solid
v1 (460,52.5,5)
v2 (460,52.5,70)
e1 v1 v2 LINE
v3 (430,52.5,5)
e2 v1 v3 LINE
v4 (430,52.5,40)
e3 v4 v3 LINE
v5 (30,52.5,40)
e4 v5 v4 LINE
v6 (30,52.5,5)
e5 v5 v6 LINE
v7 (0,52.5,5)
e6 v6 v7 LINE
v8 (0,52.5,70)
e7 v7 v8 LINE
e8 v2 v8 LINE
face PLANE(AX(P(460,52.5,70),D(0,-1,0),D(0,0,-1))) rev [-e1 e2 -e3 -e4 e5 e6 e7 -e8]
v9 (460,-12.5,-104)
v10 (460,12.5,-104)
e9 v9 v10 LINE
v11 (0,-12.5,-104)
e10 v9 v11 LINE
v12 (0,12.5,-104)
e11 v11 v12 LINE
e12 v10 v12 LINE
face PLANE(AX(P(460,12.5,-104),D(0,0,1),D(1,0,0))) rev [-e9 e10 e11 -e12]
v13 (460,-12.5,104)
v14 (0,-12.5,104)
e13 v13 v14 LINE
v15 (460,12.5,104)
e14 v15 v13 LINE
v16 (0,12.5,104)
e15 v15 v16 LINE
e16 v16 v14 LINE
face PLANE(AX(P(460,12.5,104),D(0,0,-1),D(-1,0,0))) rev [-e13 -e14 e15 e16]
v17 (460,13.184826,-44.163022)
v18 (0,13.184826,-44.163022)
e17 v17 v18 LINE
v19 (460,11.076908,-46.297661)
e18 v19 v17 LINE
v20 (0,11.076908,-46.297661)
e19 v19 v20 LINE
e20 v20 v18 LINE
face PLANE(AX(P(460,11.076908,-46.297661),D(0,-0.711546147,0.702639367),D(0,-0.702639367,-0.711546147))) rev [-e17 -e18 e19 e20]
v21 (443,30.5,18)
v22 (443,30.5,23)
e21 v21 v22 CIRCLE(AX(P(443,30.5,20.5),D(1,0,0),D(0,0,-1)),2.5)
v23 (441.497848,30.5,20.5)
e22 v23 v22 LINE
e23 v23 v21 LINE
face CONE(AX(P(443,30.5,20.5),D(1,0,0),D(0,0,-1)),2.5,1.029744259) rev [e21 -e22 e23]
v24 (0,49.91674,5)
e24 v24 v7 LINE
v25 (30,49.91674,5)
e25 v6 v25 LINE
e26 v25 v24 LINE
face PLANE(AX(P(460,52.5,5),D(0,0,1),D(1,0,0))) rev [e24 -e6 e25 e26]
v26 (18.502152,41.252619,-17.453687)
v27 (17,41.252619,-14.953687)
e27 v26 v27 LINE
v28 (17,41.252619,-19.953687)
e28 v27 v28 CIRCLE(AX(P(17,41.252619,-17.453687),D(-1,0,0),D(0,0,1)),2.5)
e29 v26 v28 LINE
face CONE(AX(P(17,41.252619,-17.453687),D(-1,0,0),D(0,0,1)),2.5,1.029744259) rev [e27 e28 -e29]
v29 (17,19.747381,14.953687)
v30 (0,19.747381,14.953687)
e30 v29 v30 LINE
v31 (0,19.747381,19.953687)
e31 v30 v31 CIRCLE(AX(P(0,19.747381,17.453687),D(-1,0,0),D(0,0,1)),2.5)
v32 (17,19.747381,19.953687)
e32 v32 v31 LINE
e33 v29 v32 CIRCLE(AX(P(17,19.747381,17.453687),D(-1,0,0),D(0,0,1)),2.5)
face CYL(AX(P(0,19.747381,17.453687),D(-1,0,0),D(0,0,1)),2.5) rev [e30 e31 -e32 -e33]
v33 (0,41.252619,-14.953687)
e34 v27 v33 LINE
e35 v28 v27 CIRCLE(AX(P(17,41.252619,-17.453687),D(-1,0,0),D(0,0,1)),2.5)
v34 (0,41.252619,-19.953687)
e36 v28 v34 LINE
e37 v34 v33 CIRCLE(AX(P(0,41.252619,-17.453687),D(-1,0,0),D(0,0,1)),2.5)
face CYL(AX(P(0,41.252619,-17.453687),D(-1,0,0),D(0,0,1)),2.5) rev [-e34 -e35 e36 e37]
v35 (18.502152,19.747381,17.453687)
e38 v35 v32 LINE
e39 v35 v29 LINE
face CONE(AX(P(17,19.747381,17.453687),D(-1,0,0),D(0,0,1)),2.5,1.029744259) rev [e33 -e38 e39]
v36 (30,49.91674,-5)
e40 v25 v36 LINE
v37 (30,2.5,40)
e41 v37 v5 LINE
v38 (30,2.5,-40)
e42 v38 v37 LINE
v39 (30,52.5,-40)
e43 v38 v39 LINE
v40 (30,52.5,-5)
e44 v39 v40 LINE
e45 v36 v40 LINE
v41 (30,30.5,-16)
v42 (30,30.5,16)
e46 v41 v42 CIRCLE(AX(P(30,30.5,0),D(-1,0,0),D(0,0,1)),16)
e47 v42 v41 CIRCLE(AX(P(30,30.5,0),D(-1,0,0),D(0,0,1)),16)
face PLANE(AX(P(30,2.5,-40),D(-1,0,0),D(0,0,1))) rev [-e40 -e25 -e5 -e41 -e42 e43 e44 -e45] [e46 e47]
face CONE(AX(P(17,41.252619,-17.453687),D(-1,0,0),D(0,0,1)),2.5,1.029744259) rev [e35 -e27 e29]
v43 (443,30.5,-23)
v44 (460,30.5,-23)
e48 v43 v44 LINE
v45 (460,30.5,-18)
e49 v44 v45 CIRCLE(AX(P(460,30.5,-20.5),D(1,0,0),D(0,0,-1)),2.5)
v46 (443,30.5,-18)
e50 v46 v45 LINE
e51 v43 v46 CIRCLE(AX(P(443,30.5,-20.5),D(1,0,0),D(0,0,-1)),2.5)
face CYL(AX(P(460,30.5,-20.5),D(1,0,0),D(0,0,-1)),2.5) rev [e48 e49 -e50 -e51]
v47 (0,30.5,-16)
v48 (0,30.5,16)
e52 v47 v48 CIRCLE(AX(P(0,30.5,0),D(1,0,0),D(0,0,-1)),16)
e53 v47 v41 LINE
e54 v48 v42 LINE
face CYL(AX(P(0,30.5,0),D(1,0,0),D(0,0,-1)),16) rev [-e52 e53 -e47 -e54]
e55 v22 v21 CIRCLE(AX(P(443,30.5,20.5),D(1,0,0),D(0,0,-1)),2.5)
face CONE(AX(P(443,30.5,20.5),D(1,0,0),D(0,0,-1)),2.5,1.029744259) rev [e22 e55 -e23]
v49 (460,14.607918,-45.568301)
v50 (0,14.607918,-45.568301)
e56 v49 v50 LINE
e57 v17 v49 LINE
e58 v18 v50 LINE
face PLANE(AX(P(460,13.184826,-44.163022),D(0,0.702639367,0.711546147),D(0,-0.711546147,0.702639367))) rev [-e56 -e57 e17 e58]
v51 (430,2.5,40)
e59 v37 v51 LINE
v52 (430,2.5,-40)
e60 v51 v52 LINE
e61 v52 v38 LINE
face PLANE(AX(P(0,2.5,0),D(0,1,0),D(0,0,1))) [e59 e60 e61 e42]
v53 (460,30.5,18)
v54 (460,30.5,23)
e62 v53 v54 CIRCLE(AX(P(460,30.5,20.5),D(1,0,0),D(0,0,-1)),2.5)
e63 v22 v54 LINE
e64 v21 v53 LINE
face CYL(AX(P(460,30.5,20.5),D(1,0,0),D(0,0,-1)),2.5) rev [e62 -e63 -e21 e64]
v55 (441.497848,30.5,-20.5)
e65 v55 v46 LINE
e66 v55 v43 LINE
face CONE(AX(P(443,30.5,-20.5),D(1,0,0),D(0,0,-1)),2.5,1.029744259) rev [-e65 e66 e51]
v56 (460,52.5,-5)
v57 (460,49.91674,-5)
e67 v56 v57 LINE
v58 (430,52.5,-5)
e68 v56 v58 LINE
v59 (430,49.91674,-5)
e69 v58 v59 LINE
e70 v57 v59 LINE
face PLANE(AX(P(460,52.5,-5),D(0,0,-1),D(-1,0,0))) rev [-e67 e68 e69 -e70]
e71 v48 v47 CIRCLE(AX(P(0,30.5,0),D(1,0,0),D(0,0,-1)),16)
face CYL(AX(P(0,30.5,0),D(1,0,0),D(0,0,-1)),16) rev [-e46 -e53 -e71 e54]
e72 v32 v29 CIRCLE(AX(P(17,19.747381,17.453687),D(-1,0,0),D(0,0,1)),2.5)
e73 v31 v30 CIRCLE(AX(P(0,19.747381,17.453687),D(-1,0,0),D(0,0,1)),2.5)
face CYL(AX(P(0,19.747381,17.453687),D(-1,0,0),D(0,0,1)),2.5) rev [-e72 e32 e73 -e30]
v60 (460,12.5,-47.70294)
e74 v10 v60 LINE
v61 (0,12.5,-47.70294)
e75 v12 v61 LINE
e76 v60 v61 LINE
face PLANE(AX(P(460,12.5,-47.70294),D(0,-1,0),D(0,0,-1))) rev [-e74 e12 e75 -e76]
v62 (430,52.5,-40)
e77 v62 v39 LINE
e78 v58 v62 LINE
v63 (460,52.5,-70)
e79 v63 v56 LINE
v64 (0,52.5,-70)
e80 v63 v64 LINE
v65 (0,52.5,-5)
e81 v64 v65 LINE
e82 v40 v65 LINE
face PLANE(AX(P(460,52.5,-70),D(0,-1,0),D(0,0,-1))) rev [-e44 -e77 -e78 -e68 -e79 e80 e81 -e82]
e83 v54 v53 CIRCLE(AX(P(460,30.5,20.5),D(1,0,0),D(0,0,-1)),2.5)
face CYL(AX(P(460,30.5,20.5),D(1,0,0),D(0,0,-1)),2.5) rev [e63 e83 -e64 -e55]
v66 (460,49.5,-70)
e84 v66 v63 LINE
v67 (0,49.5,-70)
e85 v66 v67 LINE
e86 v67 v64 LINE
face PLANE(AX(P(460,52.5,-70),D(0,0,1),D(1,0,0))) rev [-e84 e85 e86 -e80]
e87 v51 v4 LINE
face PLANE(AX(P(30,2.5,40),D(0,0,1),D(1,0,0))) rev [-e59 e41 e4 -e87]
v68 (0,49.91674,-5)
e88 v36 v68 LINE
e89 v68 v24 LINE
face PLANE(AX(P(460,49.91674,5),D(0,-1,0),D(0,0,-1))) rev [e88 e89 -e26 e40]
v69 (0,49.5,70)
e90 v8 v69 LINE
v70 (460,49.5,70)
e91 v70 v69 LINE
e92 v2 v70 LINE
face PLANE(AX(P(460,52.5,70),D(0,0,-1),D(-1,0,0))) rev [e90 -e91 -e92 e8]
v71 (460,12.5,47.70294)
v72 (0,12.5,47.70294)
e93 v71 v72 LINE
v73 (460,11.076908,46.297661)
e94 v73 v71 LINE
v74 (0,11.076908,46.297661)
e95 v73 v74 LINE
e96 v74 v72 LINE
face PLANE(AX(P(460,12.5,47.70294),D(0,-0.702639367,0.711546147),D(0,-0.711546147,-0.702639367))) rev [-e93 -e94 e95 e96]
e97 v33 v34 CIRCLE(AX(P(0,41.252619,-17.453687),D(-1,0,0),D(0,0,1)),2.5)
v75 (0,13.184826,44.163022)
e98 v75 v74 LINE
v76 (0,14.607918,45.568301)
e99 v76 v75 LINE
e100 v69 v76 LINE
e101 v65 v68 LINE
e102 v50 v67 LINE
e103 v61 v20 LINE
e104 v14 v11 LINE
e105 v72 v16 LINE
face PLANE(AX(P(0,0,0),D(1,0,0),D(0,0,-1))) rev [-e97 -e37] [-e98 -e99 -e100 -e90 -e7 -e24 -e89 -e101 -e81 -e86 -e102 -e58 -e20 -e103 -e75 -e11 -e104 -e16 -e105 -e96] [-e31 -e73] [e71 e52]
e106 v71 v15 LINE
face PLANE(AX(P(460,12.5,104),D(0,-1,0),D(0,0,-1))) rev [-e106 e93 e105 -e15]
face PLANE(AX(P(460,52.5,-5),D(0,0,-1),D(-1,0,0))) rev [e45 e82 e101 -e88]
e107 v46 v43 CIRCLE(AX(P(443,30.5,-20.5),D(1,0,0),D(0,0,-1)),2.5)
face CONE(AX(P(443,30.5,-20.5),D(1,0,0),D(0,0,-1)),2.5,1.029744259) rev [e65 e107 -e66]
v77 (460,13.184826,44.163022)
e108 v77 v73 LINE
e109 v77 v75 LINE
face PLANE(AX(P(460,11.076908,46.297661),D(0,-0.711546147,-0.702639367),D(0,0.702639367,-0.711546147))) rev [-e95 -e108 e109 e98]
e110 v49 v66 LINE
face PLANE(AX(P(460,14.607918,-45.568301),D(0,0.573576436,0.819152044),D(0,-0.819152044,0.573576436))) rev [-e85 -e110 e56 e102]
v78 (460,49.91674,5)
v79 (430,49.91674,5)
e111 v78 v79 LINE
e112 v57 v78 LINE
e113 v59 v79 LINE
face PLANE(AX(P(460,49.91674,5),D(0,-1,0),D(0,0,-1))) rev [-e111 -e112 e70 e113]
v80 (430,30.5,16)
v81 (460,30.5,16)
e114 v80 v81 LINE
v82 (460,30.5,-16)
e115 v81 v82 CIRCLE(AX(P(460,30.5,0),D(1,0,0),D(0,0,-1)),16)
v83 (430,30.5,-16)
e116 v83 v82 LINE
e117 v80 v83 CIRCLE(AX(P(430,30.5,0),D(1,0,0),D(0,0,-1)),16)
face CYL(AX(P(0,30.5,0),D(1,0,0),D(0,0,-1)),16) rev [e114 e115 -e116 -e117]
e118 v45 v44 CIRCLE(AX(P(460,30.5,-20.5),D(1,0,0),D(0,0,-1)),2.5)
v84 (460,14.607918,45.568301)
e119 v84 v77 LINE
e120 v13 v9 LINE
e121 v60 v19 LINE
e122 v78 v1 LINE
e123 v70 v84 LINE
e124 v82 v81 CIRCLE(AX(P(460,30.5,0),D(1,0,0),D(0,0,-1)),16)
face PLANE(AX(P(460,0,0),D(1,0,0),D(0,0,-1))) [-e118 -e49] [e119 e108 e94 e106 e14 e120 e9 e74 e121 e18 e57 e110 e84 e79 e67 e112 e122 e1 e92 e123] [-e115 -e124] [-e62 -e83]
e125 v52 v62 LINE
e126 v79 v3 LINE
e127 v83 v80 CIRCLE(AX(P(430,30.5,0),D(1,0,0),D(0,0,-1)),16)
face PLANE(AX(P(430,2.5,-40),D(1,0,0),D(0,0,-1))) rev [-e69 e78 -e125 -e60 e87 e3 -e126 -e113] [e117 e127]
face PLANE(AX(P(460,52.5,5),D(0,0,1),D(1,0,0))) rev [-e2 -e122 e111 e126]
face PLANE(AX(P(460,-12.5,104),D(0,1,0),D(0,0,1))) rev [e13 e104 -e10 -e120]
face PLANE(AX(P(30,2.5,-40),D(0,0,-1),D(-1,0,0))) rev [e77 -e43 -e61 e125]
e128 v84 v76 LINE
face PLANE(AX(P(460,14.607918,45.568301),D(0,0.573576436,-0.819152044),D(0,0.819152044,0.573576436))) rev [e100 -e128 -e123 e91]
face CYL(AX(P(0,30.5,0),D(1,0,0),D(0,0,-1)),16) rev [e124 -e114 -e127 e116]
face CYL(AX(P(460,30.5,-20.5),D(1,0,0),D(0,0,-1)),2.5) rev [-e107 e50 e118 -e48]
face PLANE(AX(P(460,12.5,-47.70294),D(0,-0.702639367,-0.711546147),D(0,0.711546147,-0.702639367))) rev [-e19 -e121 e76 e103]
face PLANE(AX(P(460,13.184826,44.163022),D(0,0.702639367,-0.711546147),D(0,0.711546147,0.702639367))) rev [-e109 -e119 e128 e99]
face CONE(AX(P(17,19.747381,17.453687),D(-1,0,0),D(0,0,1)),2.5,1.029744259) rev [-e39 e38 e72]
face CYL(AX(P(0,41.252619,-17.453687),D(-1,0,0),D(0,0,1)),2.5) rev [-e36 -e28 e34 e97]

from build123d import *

# Parameters (mm, degrees)
BOSS_EXTRUDE1_DEPTH   = 460
SKETCH2_W             = 400
SKETCH2_H             = 80
CUT_EXTRUDE1_DEPTH    = 50
SKETCH3_R             = 16
CUT_EXTRUDE2_DEPTH    = 475.523181731
M6_TAPPED_HOLE1_D     = 5
M6_TAPPED_HOLE1_DEPTH = 17
M6_TAPPED_HOLE1_TIP   = 1.502151548
M6_TAPPED_HOLE2_D     = 5
M6_TAPPED_HOLE2_DEPTH = 17
M6_TAPPED_HOLE2_TIP   = 1.502151548


with BuildPart() as part:
    # Sketch1 → Boss-Extrude1 (new body)
    with BuildSketch(Plane(origin=(0, 0, 0), x_dir=(0, 0, -1), z_dir=(1, 0, 0))):
        Polygon((-104, 12.5), (-47.702939672, 12.5), (-46.297660938, 11.076907706), (-44.163022497, 13.184825808), (-45.568301231, 14.607918102), (-70, 49.5), (-70, 52.5), (-5, 52.5), (-5, 49.916740154), (5, 49.916740154), (5, 52.5), (70, 52.5), (70, 49.5), (45.568301231, 14.607918102), (44.163022497, 13.184825808), (46.297660938, 11.076907706), (47.702939672, 12.5), (104, 12.5), (104, -12.5), (-104, -12.5), align=None)
    extrude(amount=BOSS_EXTRUDE1_DEPTH)

    # Sketch2 → Cut-Extrude1 (cut)
    with BuildSketch(Plane(origin=(0, 52.5, 0), x_dir=(1, 0, 0), z_dir=(0, 1, 0))):
        with Locations((230, 0)):
            Rectangle(SKETCH2_W, SKETCH2_H)
    extrude(amount=-CUT_EXTRUDE1_DEPTH, mode=Mode.SUBTRACT)

    # Sketch3 → Cut-Extrude2 (cut, through all)
    with BuildSketch(Plane(origin=(460, 0, 0), x_dir=(0, 0, -1), z_dir=(1, 0, 0))):
        with Locations((0, 30.5)):
            Circle(SKETCH3_R)
    extrude(amount=-CUT_EXTRUDE2_DEPTH, mode=Mode.SUBTRACT)

    # M6 Tapped Hole1
    with Locations(Plane(origin=(460, 0, 0), x_dir=(0, 0, -1), z_dir=(1, 0, 0))):
        with Locations((-20.5, 30.5), (20.5, 30.5)):
            Hole(M6_TAPPED_HOLE1_D / 2, depth=M6_TAPPED_HOLE1_DEPTH)
            with Locations((0, 0, -(M6_TAPPED_HOLE1_DEPTH + M6_TAPPED_HOLE1_TIP / 2))):  # 118° drill point
                Cone(0, M6_TAPPED_HOLE1_D / 2, M6_TAPPED_HOLE1_TIP, mode=Mode.SUBTRACT)

    # M6 Tapped Hole2
    with Locations(Plane.ZY):
        with Locations((17.453686729, 19.747381031), (-17.453687008, 41.252618969)):
            Hole(M6_TAPPED_HOLE2_D / 2, depth=M6_TAPPED_HOLE2_DEPTH)
            with Locations((0, 0, -(M6_TAPPED_HOLE2_DEPTH + M6_TAPPED_HOLE2_TIP / 2))):  # 118° drill point
                Cone(0, M6_TAPPED_HOLE2_D / 2, M6_TAPPED_HOLE2_TIP, mode=Mode.SUBTRACT)


solid = part.part
